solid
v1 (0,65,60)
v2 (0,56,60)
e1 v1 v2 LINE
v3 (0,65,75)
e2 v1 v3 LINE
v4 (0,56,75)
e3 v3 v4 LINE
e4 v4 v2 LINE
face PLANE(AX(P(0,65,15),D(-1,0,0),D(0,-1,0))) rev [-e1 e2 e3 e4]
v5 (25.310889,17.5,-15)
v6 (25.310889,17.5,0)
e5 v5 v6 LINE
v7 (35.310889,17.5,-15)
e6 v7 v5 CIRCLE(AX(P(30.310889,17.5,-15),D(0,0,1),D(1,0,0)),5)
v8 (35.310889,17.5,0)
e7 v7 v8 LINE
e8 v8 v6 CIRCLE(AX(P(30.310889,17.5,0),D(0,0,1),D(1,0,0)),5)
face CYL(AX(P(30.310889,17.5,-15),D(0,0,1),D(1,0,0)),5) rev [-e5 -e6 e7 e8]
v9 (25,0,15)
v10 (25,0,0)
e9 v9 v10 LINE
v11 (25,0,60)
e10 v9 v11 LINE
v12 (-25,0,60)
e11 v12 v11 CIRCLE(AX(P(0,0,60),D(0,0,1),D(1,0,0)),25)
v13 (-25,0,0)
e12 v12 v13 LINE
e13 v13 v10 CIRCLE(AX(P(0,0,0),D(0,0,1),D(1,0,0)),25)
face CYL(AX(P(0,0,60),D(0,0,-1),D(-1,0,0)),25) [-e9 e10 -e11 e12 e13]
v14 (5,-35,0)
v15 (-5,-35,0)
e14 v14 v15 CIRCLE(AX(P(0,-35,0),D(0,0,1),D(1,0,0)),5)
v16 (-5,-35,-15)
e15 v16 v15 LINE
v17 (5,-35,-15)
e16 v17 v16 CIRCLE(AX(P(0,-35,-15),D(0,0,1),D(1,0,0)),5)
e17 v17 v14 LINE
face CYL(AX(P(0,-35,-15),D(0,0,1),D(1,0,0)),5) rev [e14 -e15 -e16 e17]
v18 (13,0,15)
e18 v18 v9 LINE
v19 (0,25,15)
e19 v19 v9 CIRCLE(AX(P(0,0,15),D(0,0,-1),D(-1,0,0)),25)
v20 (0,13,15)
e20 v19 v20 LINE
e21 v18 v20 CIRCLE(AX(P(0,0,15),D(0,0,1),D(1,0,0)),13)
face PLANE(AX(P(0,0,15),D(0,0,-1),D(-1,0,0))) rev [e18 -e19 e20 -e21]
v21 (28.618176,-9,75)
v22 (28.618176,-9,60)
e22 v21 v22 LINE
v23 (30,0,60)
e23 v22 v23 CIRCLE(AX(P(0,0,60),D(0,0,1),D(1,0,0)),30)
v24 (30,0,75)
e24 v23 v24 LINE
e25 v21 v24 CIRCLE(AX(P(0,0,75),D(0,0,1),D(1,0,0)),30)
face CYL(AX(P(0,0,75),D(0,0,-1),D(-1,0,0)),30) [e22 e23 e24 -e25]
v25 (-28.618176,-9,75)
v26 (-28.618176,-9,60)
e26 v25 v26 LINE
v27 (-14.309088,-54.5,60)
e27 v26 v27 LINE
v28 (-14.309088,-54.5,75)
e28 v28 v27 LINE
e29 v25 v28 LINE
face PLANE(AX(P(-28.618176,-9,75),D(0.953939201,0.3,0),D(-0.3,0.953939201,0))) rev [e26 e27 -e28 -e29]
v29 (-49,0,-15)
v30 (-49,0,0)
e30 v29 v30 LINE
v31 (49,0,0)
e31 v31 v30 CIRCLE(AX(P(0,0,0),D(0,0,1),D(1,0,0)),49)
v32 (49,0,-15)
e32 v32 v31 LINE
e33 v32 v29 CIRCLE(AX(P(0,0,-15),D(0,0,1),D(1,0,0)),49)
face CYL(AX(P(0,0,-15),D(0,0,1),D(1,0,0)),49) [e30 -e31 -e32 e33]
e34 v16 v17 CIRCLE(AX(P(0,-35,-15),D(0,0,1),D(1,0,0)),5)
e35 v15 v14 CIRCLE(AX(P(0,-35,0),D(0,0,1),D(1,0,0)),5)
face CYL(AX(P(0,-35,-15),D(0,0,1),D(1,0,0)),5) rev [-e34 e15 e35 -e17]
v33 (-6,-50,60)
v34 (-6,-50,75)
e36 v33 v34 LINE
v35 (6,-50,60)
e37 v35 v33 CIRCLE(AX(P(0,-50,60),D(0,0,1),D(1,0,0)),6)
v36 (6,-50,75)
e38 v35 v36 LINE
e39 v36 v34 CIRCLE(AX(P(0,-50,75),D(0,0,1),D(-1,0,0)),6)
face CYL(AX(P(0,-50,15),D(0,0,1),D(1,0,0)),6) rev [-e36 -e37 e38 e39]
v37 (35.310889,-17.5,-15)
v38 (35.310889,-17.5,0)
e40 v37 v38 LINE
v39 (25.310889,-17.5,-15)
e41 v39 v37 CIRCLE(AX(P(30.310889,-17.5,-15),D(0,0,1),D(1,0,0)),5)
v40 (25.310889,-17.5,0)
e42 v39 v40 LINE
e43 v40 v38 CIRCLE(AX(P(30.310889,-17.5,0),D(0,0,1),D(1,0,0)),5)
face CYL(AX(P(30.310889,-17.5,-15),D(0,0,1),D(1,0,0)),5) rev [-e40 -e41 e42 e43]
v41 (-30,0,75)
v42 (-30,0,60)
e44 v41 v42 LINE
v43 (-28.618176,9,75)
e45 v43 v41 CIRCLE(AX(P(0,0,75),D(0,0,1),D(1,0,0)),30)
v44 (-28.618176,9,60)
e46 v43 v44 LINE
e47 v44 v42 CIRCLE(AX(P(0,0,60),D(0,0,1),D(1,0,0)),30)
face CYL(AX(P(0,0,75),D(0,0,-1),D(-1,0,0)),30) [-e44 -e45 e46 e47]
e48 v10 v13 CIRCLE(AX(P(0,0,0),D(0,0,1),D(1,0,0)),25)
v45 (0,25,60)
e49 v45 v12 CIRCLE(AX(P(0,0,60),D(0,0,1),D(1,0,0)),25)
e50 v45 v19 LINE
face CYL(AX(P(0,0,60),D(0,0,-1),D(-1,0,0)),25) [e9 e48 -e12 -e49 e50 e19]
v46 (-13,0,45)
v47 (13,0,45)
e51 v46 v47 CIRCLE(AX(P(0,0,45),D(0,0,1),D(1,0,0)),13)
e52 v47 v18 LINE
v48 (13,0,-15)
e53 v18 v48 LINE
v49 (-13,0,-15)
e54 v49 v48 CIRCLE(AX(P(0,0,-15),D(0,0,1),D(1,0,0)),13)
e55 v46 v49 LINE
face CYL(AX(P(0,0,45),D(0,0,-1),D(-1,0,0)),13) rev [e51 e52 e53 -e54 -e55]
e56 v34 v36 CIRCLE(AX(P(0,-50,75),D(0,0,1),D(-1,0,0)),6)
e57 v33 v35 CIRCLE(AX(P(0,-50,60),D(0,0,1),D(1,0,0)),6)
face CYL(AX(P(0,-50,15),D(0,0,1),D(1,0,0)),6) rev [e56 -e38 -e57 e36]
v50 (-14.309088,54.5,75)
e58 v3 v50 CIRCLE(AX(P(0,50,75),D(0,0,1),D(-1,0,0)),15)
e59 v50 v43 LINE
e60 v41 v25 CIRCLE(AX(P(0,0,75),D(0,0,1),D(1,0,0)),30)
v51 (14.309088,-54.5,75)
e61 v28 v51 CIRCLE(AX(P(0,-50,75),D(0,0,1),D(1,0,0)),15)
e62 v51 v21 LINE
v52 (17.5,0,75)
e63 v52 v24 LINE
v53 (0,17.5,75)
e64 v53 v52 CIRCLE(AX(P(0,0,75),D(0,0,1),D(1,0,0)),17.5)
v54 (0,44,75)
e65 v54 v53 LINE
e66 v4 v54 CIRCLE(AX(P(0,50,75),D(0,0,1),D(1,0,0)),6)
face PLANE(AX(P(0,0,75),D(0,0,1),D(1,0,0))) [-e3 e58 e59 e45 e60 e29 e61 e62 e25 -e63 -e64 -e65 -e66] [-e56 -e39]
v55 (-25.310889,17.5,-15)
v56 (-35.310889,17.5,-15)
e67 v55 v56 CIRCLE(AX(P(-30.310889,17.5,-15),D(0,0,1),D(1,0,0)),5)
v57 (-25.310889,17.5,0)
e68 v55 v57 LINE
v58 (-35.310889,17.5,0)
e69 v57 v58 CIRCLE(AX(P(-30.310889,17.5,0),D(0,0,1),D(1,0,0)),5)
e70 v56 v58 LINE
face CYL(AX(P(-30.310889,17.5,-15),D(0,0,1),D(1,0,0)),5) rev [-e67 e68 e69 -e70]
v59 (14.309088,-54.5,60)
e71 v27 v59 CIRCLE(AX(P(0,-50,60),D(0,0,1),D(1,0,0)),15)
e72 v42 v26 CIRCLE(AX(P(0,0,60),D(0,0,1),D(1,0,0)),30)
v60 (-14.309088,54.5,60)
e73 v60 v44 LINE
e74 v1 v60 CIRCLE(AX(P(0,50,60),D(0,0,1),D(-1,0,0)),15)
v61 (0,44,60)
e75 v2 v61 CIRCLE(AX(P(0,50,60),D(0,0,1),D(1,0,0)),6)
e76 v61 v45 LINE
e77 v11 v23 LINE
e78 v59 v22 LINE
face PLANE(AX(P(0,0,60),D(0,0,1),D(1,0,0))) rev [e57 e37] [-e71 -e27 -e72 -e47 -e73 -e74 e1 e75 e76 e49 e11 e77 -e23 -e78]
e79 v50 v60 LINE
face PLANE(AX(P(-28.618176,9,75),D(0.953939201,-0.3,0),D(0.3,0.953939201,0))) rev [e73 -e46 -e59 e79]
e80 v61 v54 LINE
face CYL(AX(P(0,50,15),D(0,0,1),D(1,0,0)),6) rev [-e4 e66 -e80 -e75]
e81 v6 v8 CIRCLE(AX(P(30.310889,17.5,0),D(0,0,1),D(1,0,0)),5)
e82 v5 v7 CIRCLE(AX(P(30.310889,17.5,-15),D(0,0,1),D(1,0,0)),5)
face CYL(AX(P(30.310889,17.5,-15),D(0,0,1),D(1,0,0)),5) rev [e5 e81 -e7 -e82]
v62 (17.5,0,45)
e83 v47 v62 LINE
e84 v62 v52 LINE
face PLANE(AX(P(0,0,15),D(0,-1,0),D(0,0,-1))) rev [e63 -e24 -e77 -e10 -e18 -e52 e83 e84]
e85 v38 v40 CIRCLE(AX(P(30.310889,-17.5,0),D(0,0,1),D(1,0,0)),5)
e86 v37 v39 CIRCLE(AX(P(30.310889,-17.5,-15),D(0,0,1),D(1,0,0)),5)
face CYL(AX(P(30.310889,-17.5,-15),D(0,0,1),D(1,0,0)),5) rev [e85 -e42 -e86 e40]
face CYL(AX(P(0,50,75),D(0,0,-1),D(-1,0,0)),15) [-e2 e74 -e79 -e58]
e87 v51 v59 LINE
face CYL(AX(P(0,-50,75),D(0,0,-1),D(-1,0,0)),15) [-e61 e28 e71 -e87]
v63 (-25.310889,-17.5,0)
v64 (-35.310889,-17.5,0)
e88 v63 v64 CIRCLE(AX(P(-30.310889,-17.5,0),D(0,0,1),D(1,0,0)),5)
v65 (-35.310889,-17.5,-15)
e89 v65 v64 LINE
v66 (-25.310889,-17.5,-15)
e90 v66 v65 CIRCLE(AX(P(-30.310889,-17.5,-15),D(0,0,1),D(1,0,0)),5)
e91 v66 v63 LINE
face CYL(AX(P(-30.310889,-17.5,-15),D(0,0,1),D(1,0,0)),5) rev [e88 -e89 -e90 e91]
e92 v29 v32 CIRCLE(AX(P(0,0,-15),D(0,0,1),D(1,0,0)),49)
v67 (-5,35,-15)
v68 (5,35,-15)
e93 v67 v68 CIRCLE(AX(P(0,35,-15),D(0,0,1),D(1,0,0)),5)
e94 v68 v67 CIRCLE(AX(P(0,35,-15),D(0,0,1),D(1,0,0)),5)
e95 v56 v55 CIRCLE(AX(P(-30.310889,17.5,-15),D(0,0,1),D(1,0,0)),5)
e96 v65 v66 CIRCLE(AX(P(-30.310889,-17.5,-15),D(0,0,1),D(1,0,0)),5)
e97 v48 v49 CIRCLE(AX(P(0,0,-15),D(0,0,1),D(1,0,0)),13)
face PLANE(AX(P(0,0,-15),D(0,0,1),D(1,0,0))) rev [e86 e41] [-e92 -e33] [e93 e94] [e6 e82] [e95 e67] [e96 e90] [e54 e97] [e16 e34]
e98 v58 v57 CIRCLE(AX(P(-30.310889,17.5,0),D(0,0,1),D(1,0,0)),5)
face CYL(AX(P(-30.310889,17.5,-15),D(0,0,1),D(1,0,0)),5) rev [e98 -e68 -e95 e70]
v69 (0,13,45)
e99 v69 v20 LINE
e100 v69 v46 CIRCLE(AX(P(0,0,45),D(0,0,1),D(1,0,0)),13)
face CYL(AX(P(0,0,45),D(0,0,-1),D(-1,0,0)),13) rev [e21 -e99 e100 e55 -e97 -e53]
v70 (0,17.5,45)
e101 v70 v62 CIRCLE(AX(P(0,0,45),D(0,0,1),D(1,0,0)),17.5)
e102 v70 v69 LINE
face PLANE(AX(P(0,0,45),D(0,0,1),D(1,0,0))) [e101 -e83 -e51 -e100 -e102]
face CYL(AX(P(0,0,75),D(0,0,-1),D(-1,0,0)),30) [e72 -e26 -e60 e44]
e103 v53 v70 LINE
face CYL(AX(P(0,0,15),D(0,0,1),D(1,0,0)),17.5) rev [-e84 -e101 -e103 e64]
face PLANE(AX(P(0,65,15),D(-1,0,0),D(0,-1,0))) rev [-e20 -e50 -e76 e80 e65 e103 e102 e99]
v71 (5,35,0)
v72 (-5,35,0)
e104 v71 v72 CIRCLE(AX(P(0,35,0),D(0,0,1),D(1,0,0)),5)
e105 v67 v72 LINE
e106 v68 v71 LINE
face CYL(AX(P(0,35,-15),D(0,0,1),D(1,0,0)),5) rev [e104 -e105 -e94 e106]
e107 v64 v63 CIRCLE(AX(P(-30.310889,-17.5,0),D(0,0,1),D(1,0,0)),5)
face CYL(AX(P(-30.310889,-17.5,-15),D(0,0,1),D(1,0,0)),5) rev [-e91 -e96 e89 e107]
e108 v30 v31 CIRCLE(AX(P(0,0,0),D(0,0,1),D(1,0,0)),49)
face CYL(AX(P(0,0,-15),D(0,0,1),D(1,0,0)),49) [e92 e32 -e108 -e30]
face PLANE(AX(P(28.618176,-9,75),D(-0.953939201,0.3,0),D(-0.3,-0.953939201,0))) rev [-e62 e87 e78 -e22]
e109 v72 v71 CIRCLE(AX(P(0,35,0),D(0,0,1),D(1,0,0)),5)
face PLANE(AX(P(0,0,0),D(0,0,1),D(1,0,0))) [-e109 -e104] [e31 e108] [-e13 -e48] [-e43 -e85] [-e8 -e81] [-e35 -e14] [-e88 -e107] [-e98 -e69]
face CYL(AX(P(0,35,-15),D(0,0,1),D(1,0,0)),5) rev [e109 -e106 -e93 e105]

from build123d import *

# Parameters (mm, degrees)
ROUND_FLANGE_SKETCH_98_R        = 49
ROUND_FLANGE_98X15_DEPTH        = 15
BOLT_HOLES_SKETCH_6X_10_PCD70_R = 5
BOLT_HOLES_6X_10_DEPTH          = 15
SLEEVE_SKETCH_50_R              = 25
SLEEVE_50X60_DEPTH              = 60
MOUNTING_FLANGE_DEPTH           = 15
SLEEVE_START                    = -60
SLEEVE_SECTION_CUT_DEPTH        = 60
SLOT_SKETCH_35X12_R             = 17.5
SLOT_SKETCH_35X12_R_2           = 6
SLOT_CUT_35X12_DEPTH            = 60
INNER_START                     = 30
INNER_BOSS_DEPTH                = 30
INNER_BORE_SKETCH_R             = 13
INNER_BORE_CUT_DEPTH            = 30


with BuildPart() as part:
    # Round Flange Sketch Ø98 → Round Flange Ø98x15 (new body)
    with BuildSketch(Plane.XY):
        Circle(ROUND_FLANGE_SKETCH_98_R)
    extrude(amount=-ROUND_FLANGE_98X15_DEPTH)

    # Bolt Holes Sketch 6xØ10 PCD70 → Bolt Holes 6xØ10 (cut)
    with BuildSketch(Plane.XY):
        with Locations((0, 35)):
            Circle(BOLT_HOLES_SKETCH_6X_10_PCD70_R)
        with Locations((30.310889132, 17.5)):
            Circle(BOLT_HOLES_SKETCH_6X_10_PCD70_R)
        with Locations((30.310889132, -17.5)):
            Circle(BOLT_HOLES_SKETCH_6X_10_PCD70_R)
        with Locations((0, -35)):
            Circle(BOLT_HOLES_SKETCH_6X_10_PCD70_R)
        with Locations((-30.310889132, -17.5)):
            Circle(BOLT_HOLES_SKETCH_6X_10_PCD70_R)
        with Locations((-30.310889132, 17.5)):
            Circle(BOLT_HOLES_SKETCH_6X_10_PCD70_R)
    extrude(amount=-BOLT_HOLES_6X_10_DEPTH, mode=Mode.SUBTRACT)

    # Sleeve Sketch Ø50 → Sleeve Ø50x60 (add)
    with BuildSketch(Plane.XY):
        Circle(SLEEVE_SKETCH_50_R)
    extrude(amount=SLEEVE_50X60_DEPTH)

    # Mounting Flange Sketch → Mounting Flange (add)
    with BuildSketch(Plane.XY.offset(60)):
        with BuildLine():
            Line((-28.618176043, -9), (-14.309088021, -54.5))
            ThreePointArc((-14.309088021, -54.5), (0, -65), (14.309088021, -54.5))
            Line((14.309088021, -54.5), (28.618176043, -9))
            ThreePointArc((28.618176043, -9), (30, 0), (28.618176043, 9))
            Line((28.618176043, 9), (14.309088021, 54.5))
            ThreePointArc((14.309088021, 54.5), (0, 65), (-14.309088021, 54.5))
            Line((-14.309088021, 54.5), (-28.618176043, 9))
            ThreePointArc((-28.618176043, 9), (-30, 0), (-28.618176043, -9))
        make_face()
    extrude(amount=MOUNTING_FLANGE_DEPTH)

    # Sleeve Section Cut Sketch → Sleeve Section Cut (cut)
    with BuildSketch(Plane.XY.offset(75).offset(SLEEVE_START)):
        with BuildLine():
            Line((0, 65), (0, 0))
            Line((0, 0), (30, 0))
            ThreePointArc((30, 0), (29.652531774, 4.552730978), (28.618176043, 9))
            Line((28.618176043, 9), (14.309088021, 54.5))
            ThreePointArc((14.309088021, 54.5), (8.874119675, 62.093386622), (0, 65))
        make_face()
    extrude(amount=SLEEVE_SECTION_CUT_DEPTH, mode=Mode.SUBTRACT)

    # Slot Sketch 35x12 → Slot Cut 35x12 (cut)
    with BuildSketch(Plane.XY.offset(75)):
        Circle(SLOT_SKETCH_35X12_R)
        with Locations((0, 50)):
            Circle(SLOT_SKETCH_35X12_R_2)
        with Locations((0, -50)):
            Circle(SLOT_SKETCH_35X12_R_2)
    extrude(amount=-SLOT_CUT_35X12_DEPTH, mode=Mode.SUBTRACT)

    # Inner Boss Sketch → Inner Boss (add)
    with BuildSketch(Plane.XY.offset(15).offset(INNER_START)):
        with BuildLine():
            Line((0, 13), (0, 17.5))
            ThreePointArc((0, 17.5), (-12.374368671, -12.374368671), (17.5, 0))
            Line((17.5, 0), (13, 0))
            ThreePointArc((13, 0), (-9.192388155, -9.192388155), (0, 13))
        make_face()
    extrude(amount=-INNER_BOSS_DEPTH)

    # Inner Bore Sketch → Inner Bore Cut (cut)
    with BuildSketch(Plane.XY.offset(15)):
        Circle(INNER_BORE_SKETCH_R)
    extrude(amount=-INNER_BORE_CUT_DEPTH, mode=Mode.SUBTRACT)


solid = part.part
